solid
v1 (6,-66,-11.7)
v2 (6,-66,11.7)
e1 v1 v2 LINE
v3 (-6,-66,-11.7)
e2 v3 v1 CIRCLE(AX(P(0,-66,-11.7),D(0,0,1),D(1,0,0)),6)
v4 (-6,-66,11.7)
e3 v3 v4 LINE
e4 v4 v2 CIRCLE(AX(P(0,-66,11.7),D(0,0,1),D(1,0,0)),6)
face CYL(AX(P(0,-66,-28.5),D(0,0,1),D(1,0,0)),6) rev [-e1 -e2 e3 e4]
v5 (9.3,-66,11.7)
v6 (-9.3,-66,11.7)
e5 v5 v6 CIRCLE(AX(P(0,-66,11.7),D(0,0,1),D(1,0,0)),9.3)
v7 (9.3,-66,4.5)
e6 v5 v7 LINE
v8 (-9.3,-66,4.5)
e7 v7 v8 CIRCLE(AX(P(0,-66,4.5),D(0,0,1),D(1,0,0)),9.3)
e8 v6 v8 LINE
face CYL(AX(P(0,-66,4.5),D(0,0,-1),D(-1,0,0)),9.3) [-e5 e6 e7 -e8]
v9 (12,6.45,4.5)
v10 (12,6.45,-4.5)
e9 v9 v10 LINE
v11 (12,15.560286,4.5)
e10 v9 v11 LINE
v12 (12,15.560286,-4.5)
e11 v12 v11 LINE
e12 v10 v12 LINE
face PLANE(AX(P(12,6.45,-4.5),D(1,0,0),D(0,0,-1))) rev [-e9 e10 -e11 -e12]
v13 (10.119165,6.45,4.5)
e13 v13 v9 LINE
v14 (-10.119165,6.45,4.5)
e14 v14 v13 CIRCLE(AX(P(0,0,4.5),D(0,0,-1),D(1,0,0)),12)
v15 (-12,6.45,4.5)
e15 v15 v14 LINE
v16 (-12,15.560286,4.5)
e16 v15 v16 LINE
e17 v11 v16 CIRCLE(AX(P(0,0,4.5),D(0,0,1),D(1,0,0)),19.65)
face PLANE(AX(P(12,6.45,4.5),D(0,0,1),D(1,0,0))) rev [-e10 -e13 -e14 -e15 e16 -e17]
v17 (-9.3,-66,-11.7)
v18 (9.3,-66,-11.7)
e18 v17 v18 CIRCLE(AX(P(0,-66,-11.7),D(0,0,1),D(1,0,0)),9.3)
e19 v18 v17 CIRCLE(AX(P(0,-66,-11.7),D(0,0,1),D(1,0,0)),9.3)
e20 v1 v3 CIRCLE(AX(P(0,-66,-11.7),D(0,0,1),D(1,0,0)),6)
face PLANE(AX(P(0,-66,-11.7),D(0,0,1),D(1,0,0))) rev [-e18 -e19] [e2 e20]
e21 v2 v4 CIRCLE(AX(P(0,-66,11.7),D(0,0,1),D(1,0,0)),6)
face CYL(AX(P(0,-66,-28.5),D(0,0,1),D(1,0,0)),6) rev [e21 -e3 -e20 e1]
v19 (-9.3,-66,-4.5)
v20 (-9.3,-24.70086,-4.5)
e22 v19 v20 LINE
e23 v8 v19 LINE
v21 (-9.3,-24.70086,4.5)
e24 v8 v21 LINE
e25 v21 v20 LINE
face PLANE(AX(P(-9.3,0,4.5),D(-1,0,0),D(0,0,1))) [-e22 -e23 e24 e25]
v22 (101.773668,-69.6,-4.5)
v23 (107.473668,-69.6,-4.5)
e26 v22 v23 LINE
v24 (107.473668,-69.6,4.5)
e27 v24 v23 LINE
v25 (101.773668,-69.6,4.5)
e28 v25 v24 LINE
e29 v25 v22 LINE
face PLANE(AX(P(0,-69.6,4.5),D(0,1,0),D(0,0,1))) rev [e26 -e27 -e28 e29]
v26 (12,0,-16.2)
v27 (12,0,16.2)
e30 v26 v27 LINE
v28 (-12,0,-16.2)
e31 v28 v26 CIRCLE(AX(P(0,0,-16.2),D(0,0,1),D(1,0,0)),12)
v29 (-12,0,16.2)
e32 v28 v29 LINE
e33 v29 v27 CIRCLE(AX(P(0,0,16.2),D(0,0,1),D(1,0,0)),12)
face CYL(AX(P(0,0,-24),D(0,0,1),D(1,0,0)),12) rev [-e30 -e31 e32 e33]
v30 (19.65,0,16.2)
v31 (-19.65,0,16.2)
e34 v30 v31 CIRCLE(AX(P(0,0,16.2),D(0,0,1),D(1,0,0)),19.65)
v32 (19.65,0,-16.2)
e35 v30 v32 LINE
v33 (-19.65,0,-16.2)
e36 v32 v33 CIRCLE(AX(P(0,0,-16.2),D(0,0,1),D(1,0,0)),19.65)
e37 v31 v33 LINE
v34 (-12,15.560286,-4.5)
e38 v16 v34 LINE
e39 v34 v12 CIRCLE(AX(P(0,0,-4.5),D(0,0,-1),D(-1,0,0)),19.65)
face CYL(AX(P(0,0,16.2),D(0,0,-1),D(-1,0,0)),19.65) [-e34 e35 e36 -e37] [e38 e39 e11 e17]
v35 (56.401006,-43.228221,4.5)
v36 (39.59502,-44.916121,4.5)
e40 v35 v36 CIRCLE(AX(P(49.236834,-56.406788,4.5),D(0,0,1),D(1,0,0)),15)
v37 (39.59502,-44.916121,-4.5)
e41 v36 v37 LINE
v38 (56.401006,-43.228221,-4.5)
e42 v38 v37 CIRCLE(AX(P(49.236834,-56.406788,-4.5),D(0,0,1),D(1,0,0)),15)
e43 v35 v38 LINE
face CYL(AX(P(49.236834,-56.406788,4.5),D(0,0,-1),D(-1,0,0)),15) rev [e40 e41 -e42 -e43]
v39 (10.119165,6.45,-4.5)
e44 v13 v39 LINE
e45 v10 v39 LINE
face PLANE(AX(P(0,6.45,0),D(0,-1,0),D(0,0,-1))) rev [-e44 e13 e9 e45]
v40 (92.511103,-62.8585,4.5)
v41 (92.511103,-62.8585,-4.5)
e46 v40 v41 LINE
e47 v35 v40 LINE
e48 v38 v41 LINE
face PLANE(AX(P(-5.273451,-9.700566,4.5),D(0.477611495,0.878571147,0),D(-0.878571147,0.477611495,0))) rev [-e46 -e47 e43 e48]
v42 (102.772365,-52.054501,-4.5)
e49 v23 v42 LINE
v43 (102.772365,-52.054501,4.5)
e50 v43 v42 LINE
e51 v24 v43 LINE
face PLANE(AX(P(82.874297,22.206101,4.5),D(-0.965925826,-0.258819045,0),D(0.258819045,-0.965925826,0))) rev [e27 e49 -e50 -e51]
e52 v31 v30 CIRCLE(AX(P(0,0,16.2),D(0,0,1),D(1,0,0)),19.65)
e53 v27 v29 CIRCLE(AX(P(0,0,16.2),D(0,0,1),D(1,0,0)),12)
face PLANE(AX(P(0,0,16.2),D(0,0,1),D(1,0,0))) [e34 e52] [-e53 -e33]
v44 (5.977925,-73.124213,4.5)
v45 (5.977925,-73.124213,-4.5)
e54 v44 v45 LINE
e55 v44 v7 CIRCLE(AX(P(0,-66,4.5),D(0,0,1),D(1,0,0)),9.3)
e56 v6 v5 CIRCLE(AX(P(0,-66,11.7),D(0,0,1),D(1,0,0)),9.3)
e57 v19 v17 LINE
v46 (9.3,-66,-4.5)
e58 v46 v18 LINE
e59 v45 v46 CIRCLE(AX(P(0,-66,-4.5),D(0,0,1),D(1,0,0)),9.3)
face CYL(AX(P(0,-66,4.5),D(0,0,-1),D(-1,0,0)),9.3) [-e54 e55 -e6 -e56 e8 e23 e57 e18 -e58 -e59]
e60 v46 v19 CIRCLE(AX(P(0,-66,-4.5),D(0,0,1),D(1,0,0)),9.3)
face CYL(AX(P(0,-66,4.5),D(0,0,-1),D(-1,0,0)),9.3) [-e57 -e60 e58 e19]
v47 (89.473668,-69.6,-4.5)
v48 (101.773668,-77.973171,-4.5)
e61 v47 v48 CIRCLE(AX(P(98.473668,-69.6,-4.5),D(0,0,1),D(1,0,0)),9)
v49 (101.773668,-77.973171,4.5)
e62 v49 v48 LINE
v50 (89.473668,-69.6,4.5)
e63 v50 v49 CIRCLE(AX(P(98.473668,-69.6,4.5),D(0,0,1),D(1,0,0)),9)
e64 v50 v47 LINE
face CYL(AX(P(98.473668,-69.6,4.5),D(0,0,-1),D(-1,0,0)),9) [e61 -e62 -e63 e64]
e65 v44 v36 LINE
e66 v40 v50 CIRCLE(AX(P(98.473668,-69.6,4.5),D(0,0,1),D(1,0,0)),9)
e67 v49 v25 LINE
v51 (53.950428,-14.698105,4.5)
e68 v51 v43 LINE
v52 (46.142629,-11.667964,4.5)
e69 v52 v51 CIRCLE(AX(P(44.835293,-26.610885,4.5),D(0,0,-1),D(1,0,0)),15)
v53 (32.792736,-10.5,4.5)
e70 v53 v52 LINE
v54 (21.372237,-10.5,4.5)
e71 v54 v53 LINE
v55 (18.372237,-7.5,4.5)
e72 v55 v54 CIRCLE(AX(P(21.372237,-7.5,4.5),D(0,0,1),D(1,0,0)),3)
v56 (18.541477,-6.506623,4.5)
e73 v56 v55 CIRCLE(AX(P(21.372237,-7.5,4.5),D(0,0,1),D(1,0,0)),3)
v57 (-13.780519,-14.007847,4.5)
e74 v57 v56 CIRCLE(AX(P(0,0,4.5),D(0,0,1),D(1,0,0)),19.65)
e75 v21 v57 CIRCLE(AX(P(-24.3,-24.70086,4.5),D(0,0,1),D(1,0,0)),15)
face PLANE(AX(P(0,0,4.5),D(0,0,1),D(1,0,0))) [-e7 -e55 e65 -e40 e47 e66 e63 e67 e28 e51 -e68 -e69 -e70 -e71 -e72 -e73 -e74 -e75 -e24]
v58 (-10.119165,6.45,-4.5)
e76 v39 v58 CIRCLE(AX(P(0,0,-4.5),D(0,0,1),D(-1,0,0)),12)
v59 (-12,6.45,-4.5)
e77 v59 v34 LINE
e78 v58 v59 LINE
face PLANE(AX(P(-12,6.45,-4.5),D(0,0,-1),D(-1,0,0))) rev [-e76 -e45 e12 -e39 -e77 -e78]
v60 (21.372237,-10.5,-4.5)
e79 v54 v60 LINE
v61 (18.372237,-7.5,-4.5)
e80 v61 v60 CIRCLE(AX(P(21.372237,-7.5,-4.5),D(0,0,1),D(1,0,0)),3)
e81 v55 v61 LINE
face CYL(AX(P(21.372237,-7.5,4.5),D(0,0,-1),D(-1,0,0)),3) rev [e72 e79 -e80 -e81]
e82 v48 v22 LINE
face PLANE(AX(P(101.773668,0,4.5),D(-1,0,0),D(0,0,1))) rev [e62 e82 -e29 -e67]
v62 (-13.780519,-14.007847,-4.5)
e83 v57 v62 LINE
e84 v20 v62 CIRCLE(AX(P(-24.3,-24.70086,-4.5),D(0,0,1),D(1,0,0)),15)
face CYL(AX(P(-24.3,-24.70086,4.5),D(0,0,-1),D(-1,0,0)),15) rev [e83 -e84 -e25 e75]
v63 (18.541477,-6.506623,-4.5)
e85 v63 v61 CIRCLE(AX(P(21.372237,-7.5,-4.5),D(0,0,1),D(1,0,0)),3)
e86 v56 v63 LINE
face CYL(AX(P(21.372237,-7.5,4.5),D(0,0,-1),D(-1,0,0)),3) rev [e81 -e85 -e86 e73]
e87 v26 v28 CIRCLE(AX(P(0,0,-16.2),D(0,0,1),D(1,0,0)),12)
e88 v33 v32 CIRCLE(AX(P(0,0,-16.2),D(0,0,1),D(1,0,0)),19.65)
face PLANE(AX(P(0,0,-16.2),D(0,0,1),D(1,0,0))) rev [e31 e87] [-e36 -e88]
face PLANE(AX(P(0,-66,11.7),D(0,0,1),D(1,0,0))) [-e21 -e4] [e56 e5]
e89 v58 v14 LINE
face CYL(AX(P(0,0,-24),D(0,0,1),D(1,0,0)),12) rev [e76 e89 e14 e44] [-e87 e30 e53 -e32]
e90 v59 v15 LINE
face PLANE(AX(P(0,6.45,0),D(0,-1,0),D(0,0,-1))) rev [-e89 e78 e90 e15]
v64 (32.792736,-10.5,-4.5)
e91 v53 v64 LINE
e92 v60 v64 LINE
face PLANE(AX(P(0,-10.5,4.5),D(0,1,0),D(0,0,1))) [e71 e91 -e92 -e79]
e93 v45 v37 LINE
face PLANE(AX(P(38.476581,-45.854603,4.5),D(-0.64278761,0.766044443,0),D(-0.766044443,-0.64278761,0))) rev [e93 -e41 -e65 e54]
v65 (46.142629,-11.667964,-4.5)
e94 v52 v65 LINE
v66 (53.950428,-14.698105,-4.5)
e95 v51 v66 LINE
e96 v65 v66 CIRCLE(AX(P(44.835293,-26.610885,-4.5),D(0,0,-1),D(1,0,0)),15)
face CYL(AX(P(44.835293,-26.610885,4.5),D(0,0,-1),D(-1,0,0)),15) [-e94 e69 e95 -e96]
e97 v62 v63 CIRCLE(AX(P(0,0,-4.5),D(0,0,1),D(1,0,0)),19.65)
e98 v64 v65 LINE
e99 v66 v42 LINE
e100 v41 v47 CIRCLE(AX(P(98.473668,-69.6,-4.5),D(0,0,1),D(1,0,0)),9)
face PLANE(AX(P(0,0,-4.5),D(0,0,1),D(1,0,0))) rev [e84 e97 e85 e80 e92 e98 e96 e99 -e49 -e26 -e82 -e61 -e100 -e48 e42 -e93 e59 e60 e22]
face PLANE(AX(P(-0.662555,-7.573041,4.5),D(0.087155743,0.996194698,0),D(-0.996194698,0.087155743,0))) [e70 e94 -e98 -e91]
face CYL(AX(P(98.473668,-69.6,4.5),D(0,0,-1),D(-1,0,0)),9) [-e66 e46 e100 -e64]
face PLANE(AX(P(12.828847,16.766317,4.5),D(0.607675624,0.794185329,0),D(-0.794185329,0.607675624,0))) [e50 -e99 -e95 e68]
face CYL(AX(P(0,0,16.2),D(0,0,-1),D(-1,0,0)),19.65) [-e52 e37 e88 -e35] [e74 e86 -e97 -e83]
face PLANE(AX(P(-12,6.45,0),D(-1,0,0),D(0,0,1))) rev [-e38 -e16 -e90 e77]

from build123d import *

# Parameters (mm, degrees)
HUB_SKETCH_R        = 19.65
HUB_39_3_DEPTH      = 16.2
LEVER_ARM_DEPTH     = 4.5
PIN_BOSS_DEPTH      = 7.2
PIN_BOSS_DEPTH_BACK = 16.2
PIN_BOSS_SKETCH_R   = 9.3
PIN_HOLE_SKETCH_R   = 6
PIN_HOLE_DEPTH      = 40.2
HUB_BORE_SKETCH_R   = 12
HUB_BORE_DEPTH      = 40.2
HUB_SLOT_DEPTH      = 13.2


with BuildPart() as part:
    # Hub Sketch → Hub Ø39.3 (new, symmetric)
    with BuildSketch(Plane.XY):
        Circle(HUB_SKETCH_R)
    extrude(amount=HUB_39_3_DEPTH, both=True)

    # Lever Arm Sketch → Lever Arm (add, symmetric)
    with BuildSketch(Plane.XY):
        with BuildLine():
            Line((-9.3, -24.700860309), (-9.3, -66))
            ThreePointArc((-9.3, -66), (-3.930349834, -74.428662419), (5.97792477, -73.124213321))
            Line((5.97792477, -73.124213321), (39.595019689, -44.916121374))
            ThreePointArc((39.595019689, -44.916121374), (47.737857787, -41.481873588), (56.401006262, -43.228220821))
            Line((56.401006262, -43.228220821), (92.511102657, -62.858500278))
            ThreePointArc((92.511102657, -62.858500278), (90.79997011, -74.302591391), (101.773667668, -77.973171442))
            Line((101.773667668, -77.973171442), (101.773667668, -69.6))
            Line((101.773667668, -69.6), (107.473667668, -69.6))
            Line((107.473667668, -69.6), (106.267896302, -65.1))
            Line((106.267896302, -65.1), (102.772365267, -52.054500578))
            Line((102.772365267, -52.054500578), (53.950427648, -14.698104885))
            ThreePointArc((53.950427648, -14.698104885), (50.262300823, -12.627051677), (46.142629433, -11.667964344))
            Line((46.142629433, -11.667964344), (32.79273589, -10.5))
            Line((32.79273589, -10.5), (21.372236663, -10.5))
            ThreePointArc((21.372236663, -10.5), (18.924775484, -9.234916071), (18.541476841, -6.506622517))
            ThreePointArc((18.541476841, -6.506622517), (4.442271, -19.141283352), (-13.780519481, -14.007847188))
            ThreePointArc((-13.780519481, -14.007847188), (-10.465401925, -18.903973549), (-9.3, -24.700860309))
        make_face()
    extrude(amount=LEVER_ARM_DEPTH, both=True)

    # Pin Boss Sketch → Pin Boss (add, two sides: drawn at the far end of the back side and taken through both)
    with BuildSketch(Plane.XY.offset(4.5).offset(-PIN_BOSS_DEPTH_BACK)):
        with Locations((0, -66)):
            Circle(PIN_BOSS_SKETCH_R)
    extrude(amount=PIN_BOSS_DEPTH + PIN_BOSS_DEPTH_BACK)

    # Pin Hole Sketch → Pin Hole (cut)
    with BuildSketch(Plane.XY.offset(11.7)):
        with Locations((0, -66)):
            Circle(PIN_HOLE_SKETCH_R)
    extrude(amount=-PIN_HOLE_DEPTH, mode=Mode.SUBTRACT)

    # Hub Bore Sketch → Hub Bore (cut)
    with BuildSketch(Plane.XY.offset(16.2)):
        Circle(HUB_BORE_SKETCH_R)
    extrude(amount=-HUB_BORE_DEPTH, mode=Mode.SUBTRACT)

    # Hub Slot Sketch → Hub Slot (cut)
    with BuildSketch(Plane(origin=(0, 19.65, 0), x_dir=(1, 0, 0), z_dir=(0, 1, 0))):
        Polygon((-12, 0), (-12, 4.5), (12, 4.5), (12, -4.5), (-12, -4.5), align=None)
    extrude(amount=-HUB_SLOT_DEPTH, mode=Mode.SUBTRACT)


solid = part.part
